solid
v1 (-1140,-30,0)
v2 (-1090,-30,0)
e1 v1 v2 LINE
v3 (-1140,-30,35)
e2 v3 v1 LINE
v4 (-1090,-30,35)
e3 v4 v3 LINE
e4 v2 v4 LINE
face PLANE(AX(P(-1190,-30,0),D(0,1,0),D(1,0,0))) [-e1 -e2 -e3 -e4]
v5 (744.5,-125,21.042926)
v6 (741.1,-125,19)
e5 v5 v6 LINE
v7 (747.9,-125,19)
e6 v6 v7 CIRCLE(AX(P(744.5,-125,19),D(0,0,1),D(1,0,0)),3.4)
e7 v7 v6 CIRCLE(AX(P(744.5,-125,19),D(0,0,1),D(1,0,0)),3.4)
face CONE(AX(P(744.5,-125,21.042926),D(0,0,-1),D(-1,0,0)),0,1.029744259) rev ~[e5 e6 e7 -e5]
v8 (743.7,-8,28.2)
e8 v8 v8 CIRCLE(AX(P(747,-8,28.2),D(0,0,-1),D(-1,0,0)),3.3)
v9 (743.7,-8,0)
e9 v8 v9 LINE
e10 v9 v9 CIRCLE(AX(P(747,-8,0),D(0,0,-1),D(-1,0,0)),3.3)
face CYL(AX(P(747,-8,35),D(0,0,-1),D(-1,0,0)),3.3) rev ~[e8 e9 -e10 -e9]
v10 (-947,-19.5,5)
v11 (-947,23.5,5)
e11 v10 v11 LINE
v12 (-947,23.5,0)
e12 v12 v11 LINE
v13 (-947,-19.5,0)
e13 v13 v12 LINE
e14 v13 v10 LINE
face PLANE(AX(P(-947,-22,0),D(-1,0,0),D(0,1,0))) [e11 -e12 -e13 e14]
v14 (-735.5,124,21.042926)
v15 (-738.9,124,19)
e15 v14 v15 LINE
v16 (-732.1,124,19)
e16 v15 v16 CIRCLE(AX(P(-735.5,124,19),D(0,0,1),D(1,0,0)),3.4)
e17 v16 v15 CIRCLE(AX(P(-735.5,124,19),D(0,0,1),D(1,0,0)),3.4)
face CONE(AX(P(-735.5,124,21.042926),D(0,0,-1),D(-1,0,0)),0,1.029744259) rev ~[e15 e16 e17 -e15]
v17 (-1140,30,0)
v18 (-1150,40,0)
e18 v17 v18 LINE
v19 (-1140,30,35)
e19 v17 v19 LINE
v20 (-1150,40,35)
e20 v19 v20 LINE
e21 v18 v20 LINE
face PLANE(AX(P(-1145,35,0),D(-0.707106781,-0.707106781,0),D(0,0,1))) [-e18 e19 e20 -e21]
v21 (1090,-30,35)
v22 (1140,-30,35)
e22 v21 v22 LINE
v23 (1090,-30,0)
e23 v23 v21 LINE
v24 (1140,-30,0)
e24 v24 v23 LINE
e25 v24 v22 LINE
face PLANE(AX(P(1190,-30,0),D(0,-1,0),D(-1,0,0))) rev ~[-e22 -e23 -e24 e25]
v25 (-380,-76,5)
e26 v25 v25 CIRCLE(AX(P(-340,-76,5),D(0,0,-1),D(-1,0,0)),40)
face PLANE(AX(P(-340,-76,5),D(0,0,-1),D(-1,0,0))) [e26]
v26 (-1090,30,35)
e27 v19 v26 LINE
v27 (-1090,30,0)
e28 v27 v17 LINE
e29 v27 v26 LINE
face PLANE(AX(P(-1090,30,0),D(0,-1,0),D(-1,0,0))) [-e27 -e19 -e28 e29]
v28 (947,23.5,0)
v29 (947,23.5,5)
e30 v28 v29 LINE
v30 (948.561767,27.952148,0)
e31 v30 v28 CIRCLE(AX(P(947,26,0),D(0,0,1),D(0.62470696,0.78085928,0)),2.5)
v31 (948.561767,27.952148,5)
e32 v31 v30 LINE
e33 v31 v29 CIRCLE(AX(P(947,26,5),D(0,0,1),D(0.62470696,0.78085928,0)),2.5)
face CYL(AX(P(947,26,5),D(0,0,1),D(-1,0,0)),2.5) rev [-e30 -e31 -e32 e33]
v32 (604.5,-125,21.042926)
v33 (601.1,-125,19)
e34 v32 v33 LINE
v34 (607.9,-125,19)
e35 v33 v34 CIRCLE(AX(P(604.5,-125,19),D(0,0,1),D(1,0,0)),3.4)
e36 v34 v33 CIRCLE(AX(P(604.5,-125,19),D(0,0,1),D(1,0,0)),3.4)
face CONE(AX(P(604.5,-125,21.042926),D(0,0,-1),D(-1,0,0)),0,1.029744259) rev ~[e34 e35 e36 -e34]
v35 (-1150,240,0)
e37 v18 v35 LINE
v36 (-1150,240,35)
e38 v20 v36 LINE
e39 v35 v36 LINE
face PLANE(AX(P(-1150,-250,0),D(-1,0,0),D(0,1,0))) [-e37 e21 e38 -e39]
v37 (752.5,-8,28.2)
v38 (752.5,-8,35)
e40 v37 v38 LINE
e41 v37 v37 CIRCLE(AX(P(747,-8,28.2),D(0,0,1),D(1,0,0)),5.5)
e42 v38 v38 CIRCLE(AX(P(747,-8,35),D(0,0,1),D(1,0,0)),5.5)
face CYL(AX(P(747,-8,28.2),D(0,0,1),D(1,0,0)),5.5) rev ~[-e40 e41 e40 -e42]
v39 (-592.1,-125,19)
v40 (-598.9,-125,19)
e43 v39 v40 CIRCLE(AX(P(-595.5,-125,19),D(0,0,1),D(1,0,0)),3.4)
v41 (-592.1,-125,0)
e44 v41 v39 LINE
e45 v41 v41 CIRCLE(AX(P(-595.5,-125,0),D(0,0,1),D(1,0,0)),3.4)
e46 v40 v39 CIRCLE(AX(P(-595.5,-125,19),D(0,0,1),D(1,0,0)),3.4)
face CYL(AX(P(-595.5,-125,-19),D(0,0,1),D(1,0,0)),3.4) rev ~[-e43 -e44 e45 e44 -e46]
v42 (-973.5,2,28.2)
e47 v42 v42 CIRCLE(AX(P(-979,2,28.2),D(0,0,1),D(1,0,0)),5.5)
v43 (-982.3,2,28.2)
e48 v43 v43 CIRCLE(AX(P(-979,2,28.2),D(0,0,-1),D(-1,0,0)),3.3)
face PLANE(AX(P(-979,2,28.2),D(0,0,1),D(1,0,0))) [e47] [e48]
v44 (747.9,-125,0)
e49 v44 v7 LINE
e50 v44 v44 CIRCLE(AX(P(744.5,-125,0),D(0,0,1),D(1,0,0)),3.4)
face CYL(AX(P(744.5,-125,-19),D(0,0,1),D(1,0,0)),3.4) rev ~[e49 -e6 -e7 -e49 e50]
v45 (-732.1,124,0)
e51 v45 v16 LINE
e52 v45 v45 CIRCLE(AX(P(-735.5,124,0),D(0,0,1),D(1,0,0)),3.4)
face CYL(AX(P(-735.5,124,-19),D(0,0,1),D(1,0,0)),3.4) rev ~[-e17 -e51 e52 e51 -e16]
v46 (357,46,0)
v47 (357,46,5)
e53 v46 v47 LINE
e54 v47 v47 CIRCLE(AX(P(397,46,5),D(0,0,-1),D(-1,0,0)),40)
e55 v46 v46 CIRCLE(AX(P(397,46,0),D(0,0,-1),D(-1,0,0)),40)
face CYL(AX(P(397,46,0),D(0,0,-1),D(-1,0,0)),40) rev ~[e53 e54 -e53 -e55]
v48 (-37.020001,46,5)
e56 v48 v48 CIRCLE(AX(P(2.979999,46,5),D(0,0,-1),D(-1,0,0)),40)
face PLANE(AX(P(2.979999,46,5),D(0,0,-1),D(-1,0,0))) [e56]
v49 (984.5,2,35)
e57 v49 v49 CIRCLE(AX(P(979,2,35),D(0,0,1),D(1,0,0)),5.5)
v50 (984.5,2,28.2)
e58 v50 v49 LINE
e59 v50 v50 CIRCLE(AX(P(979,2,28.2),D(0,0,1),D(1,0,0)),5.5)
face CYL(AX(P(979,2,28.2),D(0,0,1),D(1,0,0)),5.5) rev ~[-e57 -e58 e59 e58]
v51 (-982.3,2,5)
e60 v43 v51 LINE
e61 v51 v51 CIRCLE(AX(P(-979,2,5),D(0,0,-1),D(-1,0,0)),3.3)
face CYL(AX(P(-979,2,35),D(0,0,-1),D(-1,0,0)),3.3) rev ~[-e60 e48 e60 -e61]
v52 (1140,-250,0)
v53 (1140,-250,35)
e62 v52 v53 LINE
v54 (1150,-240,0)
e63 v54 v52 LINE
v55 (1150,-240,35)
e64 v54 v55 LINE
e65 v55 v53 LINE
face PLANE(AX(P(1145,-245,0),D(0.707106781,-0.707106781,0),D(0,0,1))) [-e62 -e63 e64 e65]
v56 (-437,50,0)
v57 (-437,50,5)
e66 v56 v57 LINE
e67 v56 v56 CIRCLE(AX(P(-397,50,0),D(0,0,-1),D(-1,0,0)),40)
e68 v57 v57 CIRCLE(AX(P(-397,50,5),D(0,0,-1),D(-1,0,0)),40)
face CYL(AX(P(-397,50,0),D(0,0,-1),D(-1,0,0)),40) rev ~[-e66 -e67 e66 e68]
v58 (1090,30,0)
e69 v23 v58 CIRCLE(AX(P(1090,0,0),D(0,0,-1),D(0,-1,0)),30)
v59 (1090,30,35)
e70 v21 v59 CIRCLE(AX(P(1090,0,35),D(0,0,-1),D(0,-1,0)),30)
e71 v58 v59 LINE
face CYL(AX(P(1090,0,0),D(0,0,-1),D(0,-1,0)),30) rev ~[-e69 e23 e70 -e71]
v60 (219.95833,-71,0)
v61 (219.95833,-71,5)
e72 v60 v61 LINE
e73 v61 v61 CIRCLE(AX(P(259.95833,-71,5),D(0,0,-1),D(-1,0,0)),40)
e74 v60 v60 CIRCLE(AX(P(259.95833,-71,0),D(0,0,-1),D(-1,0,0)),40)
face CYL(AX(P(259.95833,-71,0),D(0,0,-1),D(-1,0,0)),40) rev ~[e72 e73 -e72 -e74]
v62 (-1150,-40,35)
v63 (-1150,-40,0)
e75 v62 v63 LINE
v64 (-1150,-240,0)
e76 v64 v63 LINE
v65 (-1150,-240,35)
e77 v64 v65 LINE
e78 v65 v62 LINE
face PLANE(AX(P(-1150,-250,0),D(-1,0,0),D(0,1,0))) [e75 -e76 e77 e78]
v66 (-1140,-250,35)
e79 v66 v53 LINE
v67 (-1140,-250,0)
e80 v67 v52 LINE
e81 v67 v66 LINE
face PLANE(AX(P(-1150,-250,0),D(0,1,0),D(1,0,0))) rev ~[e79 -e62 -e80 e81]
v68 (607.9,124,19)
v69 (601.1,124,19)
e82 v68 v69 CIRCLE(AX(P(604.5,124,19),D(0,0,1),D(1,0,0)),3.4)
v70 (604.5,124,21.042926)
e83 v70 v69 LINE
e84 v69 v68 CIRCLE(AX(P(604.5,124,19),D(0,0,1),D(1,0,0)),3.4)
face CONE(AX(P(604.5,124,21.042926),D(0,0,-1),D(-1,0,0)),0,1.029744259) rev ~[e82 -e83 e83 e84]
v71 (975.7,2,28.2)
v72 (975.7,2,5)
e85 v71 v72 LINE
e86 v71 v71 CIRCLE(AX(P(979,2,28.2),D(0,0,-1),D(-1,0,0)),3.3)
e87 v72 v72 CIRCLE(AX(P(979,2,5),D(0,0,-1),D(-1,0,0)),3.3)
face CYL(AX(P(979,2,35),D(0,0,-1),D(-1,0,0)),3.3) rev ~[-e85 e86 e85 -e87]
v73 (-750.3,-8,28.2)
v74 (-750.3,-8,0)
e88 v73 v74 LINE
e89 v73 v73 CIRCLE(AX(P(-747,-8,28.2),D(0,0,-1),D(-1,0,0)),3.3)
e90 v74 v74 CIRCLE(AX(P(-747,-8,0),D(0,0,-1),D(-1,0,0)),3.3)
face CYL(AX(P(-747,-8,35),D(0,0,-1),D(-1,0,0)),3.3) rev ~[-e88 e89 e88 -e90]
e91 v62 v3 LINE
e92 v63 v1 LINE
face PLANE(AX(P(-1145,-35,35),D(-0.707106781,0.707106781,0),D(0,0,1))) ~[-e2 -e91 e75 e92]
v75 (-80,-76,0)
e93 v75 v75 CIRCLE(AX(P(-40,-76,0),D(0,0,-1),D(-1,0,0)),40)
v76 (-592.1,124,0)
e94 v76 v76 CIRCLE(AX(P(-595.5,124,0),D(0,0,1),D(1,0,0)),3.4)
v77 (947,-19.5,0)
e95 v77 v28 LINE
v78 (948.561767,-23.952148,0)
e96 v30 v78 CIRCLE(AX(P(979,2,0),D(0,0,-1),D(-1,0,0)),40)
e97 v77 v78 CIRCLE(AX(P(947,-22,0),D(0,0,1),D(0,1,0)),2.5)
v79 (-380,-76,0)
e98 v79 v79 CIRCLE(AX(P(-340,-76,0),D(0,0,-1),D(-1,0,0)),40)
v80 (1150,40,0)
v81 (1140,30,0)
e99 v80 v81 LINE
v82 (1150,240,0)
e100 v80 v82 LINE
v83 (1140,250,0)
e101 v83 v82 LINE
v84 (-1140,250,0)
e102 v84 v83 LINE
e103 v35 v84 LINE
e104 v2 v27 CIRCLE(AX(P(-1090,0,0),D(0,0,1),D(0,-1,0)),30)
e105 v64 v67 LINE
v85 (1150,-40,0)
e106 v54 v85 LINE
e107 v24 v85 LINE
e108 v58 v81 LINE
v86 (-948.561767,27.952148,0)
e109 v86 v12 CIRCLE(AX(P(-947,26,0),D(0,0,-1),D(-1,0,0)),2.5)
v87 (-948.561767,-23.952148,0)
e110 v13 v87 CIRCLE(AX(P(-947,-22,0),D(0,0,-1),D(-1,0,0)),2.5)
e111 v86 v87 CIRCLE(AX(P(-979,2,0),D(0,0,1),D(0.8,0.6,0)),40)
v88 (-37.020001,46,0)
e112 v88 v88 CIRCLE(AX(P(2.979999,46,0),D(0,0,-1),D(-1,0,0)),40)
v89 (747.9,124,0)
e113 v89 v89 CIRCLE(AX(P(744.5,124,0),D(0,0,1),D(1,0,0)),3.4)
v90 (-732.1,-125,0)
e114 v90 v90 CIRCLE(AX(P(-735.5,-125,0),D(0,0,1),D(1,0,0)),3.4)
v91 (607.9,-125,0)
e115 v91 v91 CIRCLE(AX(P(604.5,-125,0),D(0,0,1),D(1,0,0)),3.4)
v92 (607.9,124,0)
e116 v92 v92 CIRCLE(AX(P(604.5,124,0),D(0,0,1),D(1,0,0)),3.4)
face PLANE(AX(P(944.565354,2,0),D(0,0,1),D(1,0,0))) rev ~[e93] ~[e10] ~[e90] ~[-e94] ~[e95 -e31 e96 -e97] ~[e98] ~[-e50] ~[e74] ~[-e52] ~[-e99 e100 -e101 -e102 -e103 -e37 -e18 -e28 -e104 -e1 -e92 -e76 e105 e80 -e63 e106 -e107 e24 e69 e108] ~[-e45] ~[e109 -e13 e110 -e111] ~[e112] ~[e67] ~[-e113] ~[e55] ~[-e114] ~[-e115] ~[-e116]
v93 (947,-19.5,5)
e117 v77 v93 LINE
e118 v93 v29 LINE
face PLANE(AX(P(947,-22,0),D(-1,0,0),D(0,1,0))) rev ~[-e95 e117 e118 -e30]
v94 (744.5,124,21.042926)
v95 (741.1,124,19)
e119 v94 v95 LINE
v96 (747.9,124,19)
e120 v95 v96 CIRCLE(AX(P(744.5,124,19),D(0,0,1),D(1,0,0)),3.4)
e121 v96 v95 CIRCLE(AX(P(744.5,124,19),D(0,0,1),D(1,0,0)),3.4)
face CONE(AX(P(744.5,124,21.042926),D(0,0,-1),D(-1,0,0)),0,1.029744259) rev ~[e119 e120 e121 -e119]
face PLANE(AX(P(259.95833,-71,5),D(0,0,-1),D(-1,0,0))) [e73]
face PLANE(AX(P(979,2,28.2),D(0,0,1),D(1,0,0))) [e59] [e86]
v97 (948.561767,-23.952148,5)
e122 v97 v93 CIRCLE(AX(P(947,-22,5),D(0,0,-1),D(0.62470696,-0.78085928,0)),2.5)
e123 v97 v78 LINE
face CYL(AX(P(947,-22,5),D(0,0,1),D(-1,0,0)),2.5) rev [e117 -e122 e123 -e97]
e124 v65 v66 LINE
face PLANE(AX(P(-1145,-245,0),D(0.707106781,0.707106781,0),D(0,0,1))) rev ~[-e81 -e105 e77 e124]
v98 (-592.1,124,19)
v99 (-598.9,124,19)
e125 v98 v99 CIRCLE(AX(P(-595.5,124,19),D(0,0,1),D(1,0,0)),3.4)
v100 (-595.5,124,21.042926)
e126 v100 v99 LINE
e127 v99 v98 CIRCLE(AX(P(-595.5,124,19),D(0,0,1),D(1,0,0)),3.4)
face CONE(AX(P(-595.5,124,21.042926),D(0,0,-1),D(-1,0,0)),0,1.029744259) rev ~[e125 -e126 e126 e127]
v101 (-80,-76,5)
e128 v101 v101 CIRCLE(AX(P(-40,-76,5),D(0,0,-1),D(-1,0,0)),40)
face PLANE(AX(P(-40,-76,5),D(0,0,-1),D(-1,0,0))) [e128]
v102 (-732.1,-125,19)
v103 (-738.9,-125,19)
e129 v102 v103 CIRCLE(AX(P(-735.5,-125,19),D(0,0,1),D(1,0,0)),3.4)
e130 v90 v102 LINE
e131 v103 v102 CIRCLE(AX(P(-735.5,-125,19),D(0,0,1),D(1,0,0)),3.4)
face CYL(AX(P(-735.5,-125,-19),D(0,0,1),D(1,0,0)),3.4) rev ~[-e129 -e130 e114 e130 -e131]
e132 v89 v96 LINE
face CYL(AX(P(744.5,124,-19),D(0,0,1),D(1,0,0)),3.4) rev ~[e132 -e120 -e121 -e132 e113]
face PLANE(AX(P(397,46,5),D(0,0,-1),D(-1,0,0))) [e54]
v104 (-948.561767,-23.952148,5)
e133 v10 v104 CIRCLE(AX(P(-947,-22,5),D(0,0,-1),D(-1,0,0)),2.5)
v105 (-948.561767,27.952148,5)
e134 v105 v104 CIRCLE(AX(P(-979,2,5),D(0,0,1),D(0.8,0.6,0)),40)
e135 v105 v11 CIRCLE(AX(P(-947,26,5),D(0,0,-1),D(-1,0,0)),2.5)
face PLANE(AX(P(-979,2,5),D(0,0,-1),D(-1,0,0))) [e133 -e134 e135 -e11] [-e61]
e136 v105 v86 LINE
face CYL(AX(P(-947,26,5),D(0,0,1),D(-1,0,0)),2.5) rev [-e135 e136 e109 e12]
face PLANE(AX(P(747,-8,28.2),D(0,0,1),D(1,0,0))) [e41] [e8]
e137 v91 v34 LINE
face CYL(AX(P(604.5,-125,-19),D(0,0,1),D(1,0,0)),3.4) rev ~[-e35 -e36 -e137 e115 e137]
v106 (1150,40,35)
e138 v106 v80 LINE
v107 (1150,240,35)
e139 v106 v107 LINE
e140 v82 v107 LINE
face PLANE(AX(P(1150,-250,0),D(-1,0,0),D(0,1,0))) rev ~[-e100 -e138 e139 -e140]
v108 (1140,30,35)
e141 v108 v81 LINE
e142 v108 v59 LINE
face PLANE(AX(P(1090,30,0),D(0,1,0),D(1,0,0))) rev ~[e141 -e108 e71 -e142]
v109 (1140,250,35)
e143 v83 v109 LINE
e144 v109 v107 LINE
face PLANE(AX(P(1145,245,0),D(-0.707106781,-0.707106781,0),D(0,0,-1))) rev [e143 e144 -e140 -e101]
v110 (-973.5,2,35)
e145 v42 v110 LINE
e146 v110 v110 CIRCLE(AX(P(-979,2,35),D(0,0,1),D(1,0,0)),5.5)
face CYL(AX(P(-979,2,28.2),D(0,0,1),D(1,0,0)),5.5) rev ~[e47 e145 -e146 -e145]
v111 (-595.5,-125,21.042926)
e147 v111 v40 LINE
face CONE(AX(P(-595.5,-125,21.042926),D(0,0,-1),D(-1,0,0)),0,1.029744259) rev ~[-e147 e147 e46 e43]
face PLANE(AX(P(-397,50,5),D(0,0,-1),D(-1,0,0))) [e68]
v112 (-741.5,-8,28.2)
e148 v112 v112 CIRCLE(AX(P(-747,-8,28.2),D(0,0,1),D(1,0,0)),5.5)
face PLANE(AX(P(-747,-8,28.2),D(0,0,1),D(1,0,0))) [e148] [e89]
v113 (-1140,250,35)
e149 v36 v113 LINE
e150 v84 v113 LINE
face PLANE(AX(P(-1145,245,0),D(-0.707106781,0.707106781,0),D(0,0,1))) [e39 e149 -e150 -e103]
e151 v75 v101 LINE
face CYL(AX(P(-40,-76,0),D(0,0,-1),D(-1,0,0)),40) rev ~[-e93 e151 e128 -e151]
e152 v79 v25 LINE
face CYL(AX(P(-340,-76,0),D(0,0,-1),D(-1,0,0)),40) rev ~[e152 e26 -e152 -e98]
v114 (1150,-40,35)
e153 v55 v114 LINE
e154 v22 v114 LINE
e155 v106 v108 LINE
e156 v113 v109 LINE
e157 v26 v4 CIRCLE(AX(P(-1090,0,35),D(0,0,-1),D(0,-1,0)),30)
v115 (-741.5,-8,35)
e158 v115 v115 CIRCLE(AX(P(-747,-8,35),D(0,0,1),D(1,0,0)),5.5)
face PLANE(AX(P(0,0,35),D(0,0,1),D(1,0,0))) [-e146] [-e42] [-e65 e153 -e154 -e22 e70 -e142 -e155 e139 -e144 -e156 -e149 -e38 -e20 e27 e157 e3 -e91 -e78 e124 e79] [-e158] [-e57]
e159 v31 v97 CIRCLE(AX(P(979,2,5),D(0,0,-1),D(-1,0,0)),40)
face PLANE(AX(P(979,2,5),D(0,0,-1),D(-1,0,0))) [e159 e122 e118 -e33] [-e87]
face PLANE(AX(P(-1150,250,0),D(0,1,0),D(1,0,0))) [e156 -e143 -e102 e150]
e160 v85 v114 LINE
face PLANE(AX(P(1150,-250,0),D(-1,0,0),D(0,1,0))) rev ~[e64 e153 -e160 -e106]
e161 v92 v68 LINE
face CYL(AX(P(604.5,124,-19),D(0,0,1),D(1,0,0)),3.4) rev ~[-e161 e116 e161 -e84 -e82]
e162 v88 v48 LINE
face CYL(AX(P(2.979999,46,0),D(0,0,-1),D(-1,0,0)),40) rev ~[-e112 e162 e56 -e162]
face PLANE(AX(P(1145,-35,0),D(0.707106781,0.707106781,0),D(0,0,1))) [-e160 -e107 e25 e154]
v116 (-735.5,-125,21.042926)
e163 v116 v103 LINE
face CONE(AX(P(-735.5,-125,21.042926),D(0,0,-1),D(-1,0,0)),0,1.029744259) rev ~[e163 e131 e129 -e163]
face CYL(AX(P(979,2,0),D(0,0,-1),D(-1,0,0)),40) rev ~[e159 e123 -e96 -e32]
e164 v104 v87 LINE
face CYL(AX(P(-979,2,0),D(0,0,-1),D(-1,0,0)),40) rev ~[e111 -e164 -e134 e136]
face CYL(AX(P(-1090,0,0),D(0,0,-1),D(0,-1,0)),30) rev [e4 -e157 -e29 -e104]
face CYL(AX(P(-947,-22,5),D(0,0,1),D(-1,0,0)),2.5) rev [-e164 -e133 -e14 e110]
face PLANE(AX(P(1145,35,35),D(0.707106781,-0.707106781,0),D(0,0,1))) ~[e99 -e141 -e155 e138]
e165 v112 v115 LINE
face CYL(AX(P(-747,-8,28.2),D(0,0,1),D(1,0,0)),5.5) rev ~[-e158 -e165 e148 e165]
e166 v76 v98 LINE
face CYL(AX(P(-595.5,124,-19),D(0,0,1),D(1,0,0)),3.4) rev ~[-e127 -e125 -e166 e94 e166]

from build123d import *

# Parameters (mm, degrees)
SKETCH1_W                                            = 2300
SKETCH1_H                                            = 500
BOSS_EXTRUDE1_DEPTH                                  = 35
SKETCH2_R                                            = 40
CUT_EXTRUDE1_DEPTH                                   = 5
BOSS_EXTRUDE2_DEPTH                                  = 5
SKETCH4_R                                            = 2.5
CUT_EXTRUDE2_DEPTH                                   = 5
CUT_EXTRUDE3_DEPTH                                   = 1178.380567191
CHAMFER1_SIZE                                        = 10
SKETCH7_R                                            = 40
CUT_EXTRUDE4_DEPTH                                   = 5
CBORE_FOR_M6_HEXAGON_SOCKET_HEAD_CAP_SCR_D           = 6.6
CBORE_FOR_M6_HEXAGON_SOCKET_HEAD_CAP_SCR_CBORE_D     = 11
CBORE_FOR_M6_HEXAGON_SOCKET_HEAD_CAP_SCR_CBORE_DEPTH = 6.8
M8_TAPPED_HOLE1_D                                    = 6.8
M8_TAPPED_HOLE1_DEPTH                                = 19
M8_TAPPED_HOLE1_TIP                                  = 2.042926105


with BuildPart() as part:
    # Sketch1 → Boss-Extrude1 (new body)
    with BuildSketch(Plane.XY):
        Rectangle(SKETCH1_W, SKETCH1_H)
    extrude(amount=BOSS_EXTRUDE1_DEPTH)

    # Sketch2 → Cut-Extrude1 (cut)
    with BuildSketch(Plane(origin=(0, 0, 0), x_dir=(-1, 0, 0), z_dir=(0, 0, -1))):
        with Locations((-979, 2)):
            Circle(SKETCH2_R)
        with Locations((979, 2)):
            Circle(SKETCH2_R)
    extrude(amount=-CUT_EXTRUDE1_DEPTH, mode=Mode.SUBTRACT)

    # Sketch3 → Boss-Extrude2 (add)
    with BuildSketch(Plane(origin=(0, 0, 0), x_dir=(-1, 0, 0), z_dir=(0, 0, -1))):
        with BuildLine():
            Line((-947, -22), (-947, 26))
            ThreePointArc((-947, 26), (-939, 2), (-947, -22))
        make_face()
        with BuildLine():
            Line((947, -22), (947, 26))
            ThreePointArc((947, 26), (939, 2), (947, -22))
        make_face()
    extrude(amount=-BOSS_EXTRUDE2_DEPTH)

    # Sketch4 → Cut-Extrude2 (cut)
    with BuildSketch(Plane(origin=(0, 0, 5), x_dir=(-1, 0, 0), z_dir=(0, 0, -1))):
        with Locations((-947, -22)):
            Circle(SKETCH4_R)
        with Locations((-947, 26)):
            Circle(SKETCH4_R)
        with Locations((947, -22)):
            Circle(SKETCH4_R)
        with Locations((947, 26)):
            Circle(SKETCH4_R)
    extrude(amount=CUT_EXTRUDE2_DEPTH, mode=Mode.SUBTRACT)

    # Sketch6 → Cut-Extrude3 (cut, through all)
    with BuildSketch(Plane(origin=(0, 0, 0), x_dir=(-1, 0, 0), z_dir=(0, 0, -1))):
        with BuildLine():
            Line((1090, 30), (1190, 30))
            ThreePointArc((1190, 30), (1220, 0), (1190, -30))
            Line((1190, -30), (1090, -30))
            ThreePointArc((1090, -30), (1060, 0), (1090, 30))
        make_face()
        with BuildLine():
            Line((-1090, 30), (-1190, 30))
            ThreePointArc((-1190, 30), (-1220, 0), (-1190, -30))
            Line((-1190, -30), (-1090, -30))
            ThreePointArc((-1090, -30), (-1060, 0), (-1090, 30))
        make_face()
    extrude(amount=-CUT_EXTRUDE3_DEPTH, mode=Mode.SUBTRACT)

    # Chamfer1
    chamfer1_edges = [part.edges().sort_by_distance(p)[0] for p in [
        (-1150, 30, 17.5),
        (-1150, -30, 17.5),
        (1150, -30, 17.5),
        (1150, 30, 17.5),
        (1150, -250, 17.5),
        (-1150, -250, 17.5),
        (-1150, 250, 17.5),
        (1150, 250, 17.5),
    ]]
    chamfer(chamfer1_edges, length=CHAMFER1_SIZE)

    # Sketch7 → Cut-Extrude4 (cut)
    with BuildSketch(Plane(origin=(0, 0, 0), x_dir=(-1, 0, 0), z_dir=(0, 0, -1))):
        with Locations((340, -76)):
            Circle(SKETCH7_R)
        with Locations((397, 50)):
            Circle(SKETCH7_R)
        with Locations((-2.9799995, 46)):
            Circle(SKETCH7_R)
        with Locations((40, -76)):
            Circle(SKETCH7_R)
        with Locations((-259.958330439, -71)):
            Circle(SKETCH7_R)
        with Locations((-397, 46)):
            Circle(SKETCH7_R)
    extrude(amount=-CUT_EXTRUDE4_DEPTH, mode=Mode.SUBTRACT)

    # CBORE for M6 Hexagon socket head cap screws1 (through all)
    with Locations(Plane.XY.offset(35)):
        with Locations((-747, -8), (747, -8), (-979, 2), (979, 2)):
            CounterBoreHole(CBORE_FOR_M6_HEXAGON_SOCKET_HEAD_CAP_SCR_D / 2, CBORE_FOR_M6_HEXAGON_SOCKET_HEAD_CAP_SCR_CBORE_D / 2, CBORE_FOR_M6_HEXAGON_SOCKET_HEAD_CAP_SCR_CBORE_DEPTH)

    # M8 Tapped Hole1
    with Locations(Plane(origin=(0, 0, 0), x_dir=(-1, 0, 0), z_dir=(0, 0, -1))):
        with Locations((735.5, -125), (595.5, -125), (735.5, 124), (595.5, 124), (-604.5, -125), (-744.5, -125), (-604.5, 124), (-744.5, 124)):
            Hole(M8_TAPPED_HOLE1_D / 2, depth=M8_TAPPED_HOLE1_DEPTH)
            with Locations((0, 0, -(M8_TAPPED_HOLE1_DEPTH + M8_TAPPED_HOLE1_TIP / 2))):  # 118° drill point
                Cone(0, M8_TAPPED_HOLE1_D / 2, M8_TAPPED_HOLE1_TIP, mode=Mode.SUBTRACT)


solid = part.part
